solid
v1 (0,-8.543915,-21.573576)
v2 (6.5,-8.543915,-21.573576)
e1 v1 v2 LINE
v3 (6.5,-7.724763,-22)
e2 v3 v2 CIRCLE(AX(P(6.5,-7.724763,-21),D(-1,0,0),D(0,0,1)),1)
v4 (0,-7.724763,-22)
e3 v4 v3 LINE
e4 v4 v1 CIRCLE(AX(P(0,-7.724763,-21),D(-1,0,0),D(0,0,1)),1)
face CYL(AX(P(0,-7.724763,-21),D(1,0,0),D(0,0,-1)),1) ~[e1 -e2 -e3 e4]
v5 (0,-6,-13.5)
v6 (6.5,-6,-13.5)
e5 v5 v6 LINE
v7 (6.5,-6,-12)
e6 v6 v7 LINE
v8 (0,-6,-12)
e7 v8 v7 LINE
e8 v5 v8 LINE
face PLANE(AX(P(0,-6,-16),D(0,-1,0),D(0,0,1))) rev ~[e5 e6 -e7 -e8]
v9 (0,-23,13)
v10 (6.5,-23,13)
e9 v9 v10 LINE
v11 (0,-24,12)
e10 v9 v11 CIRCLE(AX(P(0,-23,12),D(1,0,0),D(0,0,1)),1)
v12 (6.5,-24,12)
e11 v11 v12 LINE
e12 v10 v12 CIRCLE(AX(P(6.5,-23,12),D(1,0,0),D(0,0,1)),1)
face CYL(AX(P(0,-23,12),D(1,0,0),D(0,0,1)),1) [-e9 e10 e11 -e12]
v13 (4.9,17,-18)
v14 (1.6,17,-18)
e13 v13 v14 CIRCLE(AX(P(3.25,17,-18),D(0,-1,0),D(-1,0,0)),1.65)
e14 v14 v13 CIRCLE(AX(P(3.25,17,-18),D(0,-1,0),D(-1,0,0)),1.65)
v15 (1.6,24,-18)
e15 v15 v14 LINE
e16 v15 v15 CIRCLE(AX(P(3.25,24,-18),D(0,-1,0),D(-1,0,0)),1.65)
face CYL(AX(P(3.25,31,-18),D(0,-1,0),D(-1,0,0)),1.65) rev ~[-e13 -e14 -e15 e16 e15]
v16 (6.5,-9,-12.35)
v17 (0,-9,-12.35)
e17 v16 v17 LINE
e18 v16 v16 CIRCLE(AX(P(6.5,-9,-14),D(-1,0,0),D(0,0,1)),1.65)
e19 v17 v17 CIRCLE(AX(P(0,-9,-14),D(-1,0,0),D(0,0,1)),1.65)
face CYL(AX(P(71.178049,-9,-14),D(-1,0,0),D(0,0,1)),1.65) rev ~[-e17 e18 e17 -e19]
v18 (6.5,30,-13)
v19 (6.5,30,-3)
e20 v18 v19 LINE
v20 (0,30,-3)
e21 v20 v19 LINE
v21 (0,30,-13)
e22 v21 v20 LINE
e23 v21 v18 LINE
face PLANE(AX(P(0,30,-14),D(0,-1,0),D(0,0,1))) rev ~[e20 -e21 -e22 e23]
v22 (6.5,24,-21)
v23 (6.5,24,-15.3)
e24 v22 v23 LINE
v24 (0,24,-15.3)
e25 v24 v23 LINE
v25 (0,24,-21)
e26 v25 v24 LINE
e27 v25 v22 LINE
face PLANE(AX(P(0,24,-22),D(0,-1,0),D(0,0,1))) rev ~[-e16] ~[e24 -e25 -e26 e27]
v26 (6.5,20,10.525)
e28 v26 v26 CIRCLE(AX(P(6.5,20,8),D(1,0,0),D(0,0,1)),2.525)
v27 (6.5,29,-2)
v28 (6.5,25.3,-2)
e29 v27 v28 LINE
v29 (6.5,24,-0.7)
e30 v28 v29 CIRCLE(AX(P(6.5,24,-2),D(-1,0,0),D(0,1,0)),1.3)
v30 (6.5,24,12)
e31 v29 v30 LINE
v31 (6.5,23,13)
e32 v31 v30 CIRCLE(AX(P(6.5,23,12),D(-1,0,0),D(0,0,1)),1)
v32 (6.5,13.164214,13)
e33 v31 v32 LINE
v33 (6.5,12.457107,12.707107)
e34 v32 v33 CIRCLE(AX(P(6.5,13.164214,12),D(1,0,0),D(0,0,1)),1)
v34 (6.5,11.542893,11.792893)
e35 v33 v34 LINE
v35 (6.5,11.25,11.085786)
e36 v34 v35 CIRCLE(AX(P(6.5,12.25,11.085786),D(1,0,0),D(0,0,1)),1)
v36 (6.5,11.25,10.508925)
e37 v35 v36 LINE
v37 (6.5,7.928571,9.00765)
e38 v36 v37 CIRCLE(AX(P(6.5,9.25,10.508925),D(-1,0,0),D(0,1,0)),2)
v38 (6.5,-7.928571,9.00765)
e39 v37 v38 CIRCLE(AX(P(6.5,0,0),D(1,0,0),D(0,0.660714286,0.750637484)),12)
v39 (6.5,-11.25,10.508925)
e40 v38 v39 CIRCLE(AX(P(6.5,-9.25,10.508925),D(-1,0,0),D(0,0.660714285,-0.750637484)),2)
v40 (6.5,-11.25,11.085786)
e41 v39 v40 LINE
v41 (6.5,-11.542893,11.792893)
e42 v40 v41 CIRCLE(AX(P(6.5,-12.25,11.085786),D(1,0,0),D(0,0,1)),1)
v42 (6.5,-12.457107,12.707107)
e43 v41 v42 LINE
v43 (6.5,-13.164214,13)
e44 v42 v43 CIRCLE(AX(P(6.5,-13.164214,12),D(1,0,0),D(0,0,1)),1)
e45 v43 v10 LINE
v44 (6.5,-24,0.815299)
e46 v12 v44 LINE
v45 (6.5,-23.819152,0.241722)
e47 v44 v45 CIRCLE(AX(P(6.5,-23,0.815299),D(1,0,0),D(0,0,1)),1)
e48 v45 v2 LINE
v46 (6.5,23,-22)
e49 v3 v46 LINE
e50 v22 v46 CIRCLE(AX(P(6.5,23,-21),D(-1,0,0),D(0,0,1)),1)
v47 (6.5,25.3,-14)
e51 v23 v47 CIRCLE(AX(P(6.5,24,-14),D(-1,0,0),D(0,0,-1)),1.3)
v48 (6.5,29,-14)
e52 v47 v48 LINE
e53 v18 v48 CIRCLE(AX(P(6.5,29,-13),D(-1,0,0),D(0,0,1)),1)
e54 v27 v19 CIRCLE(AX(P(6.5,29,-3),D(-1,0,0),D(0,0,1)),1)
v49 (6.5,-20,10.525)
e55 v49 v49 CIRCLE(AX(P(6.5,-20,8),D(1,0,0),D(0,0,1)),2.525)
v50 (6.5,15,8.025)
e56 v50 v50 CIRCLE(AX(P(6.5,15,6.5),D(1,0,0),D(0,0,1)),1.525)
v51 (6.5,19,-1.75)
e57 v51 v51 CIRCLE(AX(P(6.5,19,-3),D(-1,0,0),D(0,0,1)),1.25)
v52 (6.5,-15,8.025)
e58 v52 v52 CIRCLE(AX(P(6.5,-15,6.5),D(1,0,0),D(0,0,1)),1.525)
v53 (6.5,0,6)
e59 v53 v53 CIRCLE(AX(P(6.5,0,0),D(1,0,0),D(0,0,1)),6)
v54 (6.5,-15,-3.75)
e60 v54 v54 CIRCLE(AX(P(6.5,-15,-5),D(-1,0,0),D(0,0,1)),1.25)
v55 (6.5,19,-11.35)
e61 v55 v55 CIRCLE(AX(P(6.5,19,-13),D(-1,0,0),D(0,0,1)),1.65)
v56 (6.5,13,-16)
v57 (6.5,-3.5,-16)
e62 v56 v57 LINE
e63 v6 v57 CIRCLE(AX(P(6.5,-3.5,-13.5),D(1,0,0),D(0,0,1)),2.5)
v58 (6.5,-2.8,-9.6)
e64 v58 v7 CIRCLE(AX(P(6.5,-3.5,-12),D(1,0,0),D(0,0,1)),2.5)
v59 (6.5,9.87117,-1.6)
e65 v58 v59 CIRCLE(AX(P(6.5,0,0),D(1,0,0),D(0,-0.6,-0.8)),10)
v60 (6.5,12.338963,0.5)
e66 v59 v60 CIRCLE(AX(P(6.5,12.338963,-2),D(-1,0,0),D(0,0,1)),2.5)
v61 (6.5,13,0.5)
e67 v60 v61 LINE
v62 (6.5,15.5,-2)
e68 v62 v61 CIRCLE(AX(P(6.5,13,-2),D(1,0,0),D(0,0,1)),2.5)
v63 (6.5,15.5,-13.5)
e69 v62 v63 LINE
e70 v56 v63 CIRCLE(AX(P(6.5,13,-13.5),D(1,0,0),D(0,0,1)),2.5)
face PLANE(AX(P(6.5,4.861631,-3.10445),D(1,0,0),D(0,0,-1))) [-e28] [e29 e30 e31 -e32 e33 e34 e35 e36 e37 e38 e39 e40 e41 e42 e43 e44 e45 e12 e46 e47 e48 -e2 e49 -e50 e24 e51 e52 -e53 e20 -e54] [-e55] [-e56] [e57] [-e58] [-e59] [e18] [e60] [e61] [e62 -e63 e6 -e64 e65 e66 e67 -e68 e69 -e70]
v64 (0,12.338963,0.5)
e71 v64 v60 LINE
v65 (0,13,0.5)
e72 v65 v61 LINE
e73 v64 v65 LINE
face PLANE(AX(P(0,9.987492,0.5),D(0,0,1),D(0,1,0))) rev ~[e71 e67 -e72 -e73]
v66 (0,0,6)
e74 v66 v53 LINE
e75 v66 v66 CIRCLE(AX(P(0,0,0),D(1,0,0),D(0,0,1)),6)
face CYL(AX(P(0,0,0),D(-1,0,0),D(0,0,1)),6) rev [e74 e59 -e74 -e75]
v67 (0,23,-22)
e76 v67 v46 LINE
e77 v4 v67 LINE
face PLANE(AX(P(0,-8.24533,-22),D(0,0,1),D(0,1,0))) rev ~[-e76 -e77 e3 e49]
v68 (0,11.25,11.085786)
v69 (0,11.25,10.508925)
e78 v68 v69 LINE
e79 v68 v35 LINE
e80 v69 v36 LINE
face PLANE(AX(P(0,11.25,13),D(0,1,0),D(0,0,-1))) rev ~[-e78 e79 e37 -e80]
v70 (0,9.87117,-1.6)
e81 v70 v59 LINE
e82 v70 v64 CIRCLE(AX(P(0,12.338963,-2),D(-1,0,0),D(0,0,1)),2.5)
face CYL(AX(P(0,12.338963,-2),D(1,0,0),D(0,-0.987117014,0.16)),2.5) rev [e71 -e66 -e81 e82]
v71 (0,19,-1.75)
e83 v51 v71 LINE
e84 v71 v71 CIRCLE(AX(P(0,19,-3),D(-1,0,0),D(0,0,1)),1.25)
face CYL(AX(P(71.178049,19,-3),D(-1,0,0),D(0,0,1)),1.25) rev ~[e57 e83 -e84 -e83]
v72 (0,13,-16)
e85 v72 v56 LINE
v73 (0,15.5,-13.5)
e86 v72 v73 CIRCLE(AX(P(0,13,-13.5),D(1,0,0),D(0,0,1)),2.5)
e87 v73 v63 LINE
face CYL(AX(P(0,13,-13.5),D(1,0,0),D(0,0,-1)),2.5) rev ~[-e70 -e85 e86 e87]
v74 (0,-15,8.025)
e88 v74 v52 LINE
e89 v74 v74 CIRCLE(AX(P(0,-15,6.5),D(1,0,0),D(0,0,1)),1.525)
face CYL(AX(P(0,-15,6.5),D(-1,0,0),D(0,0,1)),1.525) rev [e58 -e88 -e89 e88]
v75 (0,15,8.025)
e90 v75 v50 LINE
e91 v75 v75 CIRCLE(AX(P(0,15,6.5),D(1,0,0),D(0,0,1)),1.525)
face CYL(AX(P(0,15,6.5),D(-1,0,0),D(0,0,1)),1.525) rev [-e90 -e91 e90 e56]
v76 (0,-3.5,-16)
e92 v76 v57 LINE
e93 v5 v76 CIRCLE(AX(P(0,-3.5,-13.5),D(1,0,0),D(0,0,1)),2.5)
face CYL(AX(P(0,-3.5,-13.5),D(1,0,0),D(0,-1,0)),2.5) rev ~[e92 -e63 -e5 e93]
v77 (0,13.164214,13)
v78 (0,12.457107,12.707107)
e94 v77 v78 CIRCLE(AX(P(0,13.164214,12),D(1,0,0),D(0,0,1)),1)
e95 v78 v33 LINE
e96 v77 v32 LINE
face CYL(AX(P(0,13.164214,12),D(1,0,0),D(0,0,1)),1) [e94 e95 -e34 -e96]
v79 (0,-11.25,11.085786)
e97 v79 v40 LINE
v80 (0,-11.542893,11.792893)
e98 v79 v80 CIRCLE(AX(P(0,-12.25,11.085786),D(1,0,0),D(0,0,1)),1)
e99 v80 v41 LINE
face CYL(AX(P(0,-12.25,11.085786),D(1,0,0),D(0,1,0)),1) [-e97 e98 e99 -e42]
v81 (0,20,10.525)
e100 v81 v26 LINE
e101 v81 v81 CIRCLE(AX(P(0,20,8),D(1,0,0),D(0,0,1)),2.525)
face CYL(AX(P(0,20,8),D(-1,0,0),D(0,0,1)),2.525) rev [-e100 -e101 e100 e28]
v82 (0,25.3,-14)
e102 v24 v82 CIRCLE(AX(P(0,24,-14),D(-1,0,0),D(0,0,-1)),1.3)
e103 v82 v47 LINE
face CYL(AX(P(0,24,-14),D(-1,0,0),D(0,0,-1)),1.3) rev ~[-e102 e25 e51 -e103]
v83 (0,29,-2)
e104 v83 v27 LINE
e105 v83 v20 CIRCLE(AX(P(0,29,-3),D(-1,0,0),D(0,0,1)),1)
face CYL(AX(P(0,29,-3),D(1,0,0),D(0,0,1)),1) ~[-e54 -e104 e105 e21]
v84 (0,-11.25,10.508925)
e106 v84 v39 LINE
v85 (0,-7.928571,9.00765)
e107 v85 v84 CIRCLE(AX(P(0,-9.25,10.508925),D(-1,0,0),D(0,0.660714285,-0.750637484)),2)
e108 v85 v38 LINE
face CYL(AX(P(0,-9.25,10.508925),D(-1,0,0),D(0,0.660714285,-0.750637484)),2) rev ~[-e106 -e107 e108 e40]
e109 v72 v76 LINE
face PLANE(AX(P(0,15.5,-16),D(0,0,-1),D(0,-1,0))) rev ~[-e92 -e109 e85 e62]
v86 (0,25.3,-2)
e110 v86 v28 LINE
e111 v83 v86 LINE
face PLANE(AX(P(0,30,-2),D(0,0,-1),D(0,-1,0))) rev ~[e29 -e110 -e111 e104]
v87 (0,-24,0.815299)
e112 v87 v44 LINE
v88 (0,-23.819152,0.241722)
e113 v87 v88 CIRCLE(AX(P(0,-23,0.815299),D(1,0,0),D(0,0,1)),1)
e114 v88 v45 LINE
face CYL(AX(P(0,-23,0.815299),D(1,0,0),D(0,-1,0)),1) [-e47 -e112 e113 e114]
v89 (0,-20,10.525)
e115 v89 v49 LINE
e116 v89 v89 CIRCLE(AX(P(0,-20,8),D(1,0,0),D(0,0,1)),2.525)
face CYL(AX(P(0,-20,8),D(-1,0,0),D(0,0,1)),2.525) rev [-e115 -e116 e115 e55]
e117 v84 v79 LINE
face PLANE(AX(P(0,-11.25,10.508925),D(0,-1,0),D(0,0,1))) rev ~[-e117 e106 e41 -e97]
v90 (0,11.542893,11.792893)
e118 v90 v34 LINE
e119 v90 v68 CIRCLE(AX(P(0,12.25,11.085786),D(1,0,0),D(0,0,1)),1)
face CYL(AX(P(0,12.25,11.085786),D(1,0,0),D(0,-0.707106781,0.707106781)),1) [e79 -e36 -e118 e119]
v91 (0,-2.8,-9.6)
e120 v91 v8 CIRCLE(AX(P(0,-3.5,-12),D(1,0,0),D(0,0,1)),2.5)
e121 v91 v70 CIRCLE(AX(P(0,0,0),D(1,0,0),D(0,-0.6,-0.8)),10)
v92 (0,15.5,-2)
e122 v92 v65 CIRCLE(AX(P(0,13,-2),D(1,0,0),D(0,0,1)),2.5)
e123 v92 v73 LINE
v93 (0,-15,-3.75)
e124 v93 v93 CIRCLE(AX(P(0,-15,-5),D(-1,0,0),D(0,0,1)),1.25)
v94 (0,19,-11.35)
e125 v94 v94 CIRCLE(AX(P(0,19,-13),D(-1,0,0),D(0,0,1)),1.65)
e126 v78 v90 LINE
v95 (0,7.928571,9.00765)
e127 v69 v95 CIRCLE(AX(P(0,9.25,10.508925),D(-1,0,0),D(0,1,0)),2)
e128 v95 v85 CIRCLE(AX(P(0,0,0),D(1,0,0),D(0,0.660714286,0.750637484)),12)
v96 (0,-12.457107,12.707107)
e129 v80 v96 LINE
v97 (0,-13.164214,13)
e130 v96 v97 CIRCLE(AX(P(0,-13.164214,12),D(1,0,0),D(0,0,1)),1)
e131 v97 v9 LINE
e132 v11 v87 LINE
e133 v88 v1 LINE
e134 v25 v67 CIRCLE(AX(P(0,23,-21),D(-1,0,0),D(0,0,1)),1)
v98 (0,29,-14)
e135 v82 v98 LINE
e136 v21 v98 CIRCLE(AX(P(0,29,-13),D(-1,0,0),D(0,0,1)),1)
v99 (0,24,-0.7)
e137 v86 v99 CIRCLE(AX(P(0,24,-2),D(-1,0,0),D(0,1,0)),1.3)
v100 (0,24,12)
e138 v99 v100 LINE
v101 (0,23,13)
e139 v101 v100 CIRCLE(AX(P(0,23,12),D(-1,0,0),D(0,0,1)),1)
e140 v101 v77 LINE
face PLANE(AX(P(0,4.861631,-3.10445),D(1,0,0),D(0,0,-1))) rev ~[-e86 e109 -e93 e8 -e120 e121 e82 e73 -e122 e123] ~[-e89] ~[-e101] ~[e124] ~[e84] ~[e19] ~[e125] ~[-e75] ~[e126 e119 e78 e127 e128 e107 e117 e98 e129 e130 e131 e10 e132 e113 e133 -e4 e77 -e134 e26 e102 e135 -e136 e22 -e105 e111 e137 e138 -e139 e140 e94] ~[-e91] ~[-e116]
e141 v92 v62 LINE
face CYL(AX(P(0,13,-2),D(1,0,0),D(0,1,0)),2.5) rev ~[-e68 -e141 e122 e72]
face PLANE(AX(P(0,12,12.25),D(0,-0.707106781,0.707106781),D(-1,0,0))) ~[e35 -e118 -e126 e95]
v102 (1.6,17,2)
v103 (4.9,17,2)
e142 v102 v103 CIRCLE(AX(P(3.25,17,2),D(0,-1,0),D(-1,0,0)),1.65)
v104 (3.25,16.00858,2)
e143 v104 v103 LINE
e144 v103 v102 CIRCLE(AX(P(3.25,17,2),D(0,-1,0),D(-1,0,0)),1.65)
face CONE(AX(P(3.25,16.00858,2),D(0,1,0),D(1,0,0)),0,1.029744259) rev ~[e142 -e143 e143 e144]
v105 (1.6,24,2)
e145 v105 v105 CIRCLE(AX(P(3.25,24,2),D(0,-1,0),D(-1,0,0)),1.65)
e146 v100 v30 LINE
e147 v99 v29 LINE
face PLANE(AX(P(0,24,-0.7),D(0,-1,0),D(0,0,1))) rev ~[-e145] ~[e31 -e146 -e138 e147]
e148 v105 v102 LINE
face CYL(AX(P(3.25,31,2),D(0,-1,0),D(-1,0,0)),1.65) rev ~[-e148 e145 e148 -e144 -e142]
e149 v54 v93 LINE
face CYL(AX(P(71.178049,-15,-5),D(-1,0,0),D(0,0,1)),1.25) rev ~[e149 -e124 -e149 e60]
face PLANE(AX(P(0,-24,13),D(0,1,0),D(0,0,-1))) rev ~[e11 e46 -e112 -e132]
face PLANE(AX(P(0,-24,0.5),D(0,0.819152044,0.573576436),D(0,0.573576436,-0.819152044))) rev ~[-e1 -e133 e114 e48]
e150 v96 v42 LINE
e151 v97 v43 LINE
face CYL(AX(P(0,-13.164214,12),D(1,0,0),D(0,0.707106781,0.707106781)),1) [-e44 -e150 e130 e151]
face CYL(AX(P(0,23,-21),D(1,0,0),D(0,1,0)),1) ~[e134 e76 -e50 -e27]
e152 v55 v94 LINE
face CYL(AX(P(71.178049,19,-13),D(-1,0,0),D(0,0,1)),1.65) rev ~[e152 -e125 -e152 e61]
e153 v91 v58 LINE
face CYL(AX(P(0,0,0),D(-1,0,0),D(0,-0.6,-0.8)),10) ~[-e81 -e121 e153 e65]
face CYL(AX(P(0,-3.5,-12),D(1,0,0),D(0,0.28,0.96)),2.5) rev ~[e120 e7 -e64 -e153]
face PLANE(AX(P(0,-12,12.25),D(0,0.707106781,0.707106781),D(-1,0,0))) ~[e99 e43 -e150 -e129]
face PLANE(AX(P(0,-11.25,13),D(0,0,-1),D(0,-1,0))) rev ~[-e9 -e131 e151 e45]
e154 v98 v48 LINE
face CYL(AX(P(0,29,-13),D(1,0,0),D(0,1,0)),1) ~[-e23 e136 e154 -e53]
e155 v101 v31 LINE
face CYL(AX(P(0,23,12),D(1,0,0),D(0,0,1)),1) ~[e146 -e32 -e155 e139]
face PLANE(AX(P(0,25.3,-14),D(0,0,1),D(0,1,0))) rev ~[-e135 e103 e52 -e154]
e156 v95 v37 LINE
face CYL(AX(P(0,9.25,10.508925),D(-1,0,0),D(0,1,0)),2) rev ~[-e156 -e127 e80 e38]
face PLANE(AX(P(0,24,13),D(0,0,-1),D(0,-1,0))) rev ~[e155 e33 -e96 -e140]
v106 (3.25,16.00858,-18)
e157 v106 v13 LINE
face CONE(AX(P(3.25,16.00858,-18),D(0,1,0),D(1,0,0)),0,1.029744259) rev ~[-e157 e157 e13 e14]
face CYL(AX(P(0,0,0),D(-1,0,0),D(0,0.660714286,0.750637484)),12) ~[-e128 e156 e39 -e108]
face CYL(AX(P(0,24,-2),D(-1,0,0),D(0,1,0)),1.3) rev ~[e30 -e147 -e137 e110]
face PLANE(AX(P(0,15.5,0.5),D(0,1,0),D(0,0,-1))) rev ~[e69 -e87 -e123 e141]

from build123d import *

# Parameters (mm, degrees)
SKETCH_1_R             = 6
SKETCH_1_R_2           = 1.525
SKETCH_1_R_3           = 2.525
EXTRUDE_1_DEPTH        = 6.5
FILLET_R2_5_1_R        = 2.5
HOLE_WIZARD_M3_1_D     = 2.5
HOLE_WIZARD_M4_1_D     = 3.3
HOLE_WIZARD_M4_1_DEPTH = 7
HOLE_WIZARD_M4_1_TIP   = 0.991420021
HOLE_WIZARD_M4_2_D     = 3.3
CHAMFER_C1_5_1_SIZE    = 1.5
FILLET_R1_2_R          = 1


with BuildPart() as part:
    # 草图1 → 凸台-拉伸1 (new body)
    with BuildSketch(Plane(origin=(0, 0, 0), x_dir=(0, 0, -1), z_dir=(1, 0, 0))):
        with BuildLine():
            Line((-13, 24), (-13, 11.25))
            Line((-13, 11.25), (-10.508924778, 11.25))
            ThreePointArc((-10.508924778, 11.25), (-8.68644609, 10.073754471), (-9.00764981, 7.928571429))
            ThreePointArc((-9.00764981, 7.928571429), (-12, 0), (-9.00764981, -7.928571429))
            ThreePointArc((-9.00764981, -7.928571429), (-8.68644609, -10.073754471), (-10.508924778, -11.25))
            Line((-10.508924778, -11.25), (-13, -11.25))
            Line((-13, -11.25), (-13, -24))
            Line((-13, -24), (-0.5, -24))
            Line((-0.5, -24), (22, -8.24533039))
            Line((22, -8.24533039), (22, 24))
            Line((22, 24), (15.3, 24))
            ThreePointArc((15.3, 24), (13.080761184, 23.080761184), (14, 25.3))
            Line((14, 25.3), (14, 30))
            Line((14, 30), (2, 30))
            Line((2, 30), (2, 25.3))
            ThreePointArc((2, 25.3), (2.919238816, 23.080761184), (0.7, 24))
            Line((0.7, 24), (-13, 24))
        make_face()
        with Locations(Location((0, 0, 0), (0, 0, 180))):
            Circle(SKETCH_1_R, mode=Mode.SUBTRACT)
        with Locations(Location((-6.5, 15, 0), (0, 0, 180))):
            Circle(SKETCH_1_R_2, mode=Mode.SUBTRACT)
        with Locations(Location((-8, 20, 0), (0, 0, 180))):
            Circle(SKETCH_1_R_3, mode=Mode.SUBTRACT)
        with Locations(Location((-6.5, -15, 0), (0, 0, 180))):
            Circle(SKETCH_1_R_2, mode=Mode.SUBTRACT)
        with Locations(Location((-8, -20, 0), (0, 0, 180))):
            Circle(SKETCH_1_R_3, mode=Mode.SUBTRACT)
        with BuildLine():
            Line((-0.5, 9.987492178), (-0.5, 15.5))
            Line((-0.5, 15.5), (16, 15.5))
            Line((16, 15.5), (16, -6))
            Line((16, -6), (8, -6))
            ThreePointArc((8, -6), (8.829636263, 4.694414071), (-0.5, 9.987492178))
        make_face(mode=Mode.SUBTRACT)
    extrude(amount=EXTRUDE_1_DEPTH)

    # R2.5 圆角1
    fillet_r2_5_1_edges = [part.edges().sort_by_distance(p)[0] for p in [
        (3.25, -6, -16),
        (3.25, 15.5, -16),
        (3.25, 15.5, 0.5),
        (3.25, 9.987492178, 0.5),
        (3.25, -6, -8),
    ]]
    fillet(fillet_r2_5_1_edges, radius=FILLET_R2_5_1_R)

    # M3 螺纹孔1 (through all)
    with Locations(Plane(origin=(6.5, 0, 0), x_dir=(0, 0, -1), z_dir=(1, 0, 0))):
        with Locations((5, -15), (3, 19)):
            Hole(HOLE_WIZARD_M3_1_D / 2)

    # M4 螺纹孔1
    with Locations(Plane(origin=(0, 24, 0), x_dir=(1, 0, 0), z_dir=(0, 1, 0))):
        with Locations((3.25, -2), (3.25, 18)):
            Hole(HOLE_WIZARD_M4_1_D / 2, depth=HOLE_WIZARD_M4_1_DEPTH)
            with Locations((0, 0, -(HOLE_WIZARD_M4_1_DEPTH + HOLE_WIZARD_M4_1_TIP / 2))):  # 118° drill point
                Cone(0, HOLE_WIZARD_M4_1_D / 2, HOLE_WIZARD_M4_1_TIP, mode=Mode.SUBTRACT)

    # M4 螺纹孔2 (through all)
    with Locations(Plane(origin=(6.5, 0, 0), x_dir=(0, 0, -1), z_dir=(1, 0, 0))):
        with Locations((14, -9), (13, 19)):
            Hole(HOLE_WIZARD_M4_2_D / 2)

    # C1.5 倒角1
    chamfer_c1_5_1_edges = [part.edges().sort_by_distance(p)[0] for p in [
        (3.25, -11.25, 13),
        (3.25, 11.25, 13),
    ]]
    chamfer(chamfer_c1_5_1_edges, length=CHAMFER_C1_5_1_SIZE)

    # R1 圆角2
    fillet_r1_2_edges = [part.edges().sort_by_distance(p)[0] for p in [
        (3.25, -12.75, 13),
        (3.25, -11.25, 11.5),
        (3.25, 11.25, 11.5),
        (3.25, 12.75, 13),
        (3.25, 30, -2),
        (3.25, 30, -14),
        (3.25, 24, -22),
        (3.25, -8.24533039, -22),
        (3.25, -24, 0.5),
        (3.25, -24, 13),
        (3.25, 24, 13),
    ]]
    fillet(fillet_r1_2_edges, radius=FILLET_R1_2_R)


solid = part.part
